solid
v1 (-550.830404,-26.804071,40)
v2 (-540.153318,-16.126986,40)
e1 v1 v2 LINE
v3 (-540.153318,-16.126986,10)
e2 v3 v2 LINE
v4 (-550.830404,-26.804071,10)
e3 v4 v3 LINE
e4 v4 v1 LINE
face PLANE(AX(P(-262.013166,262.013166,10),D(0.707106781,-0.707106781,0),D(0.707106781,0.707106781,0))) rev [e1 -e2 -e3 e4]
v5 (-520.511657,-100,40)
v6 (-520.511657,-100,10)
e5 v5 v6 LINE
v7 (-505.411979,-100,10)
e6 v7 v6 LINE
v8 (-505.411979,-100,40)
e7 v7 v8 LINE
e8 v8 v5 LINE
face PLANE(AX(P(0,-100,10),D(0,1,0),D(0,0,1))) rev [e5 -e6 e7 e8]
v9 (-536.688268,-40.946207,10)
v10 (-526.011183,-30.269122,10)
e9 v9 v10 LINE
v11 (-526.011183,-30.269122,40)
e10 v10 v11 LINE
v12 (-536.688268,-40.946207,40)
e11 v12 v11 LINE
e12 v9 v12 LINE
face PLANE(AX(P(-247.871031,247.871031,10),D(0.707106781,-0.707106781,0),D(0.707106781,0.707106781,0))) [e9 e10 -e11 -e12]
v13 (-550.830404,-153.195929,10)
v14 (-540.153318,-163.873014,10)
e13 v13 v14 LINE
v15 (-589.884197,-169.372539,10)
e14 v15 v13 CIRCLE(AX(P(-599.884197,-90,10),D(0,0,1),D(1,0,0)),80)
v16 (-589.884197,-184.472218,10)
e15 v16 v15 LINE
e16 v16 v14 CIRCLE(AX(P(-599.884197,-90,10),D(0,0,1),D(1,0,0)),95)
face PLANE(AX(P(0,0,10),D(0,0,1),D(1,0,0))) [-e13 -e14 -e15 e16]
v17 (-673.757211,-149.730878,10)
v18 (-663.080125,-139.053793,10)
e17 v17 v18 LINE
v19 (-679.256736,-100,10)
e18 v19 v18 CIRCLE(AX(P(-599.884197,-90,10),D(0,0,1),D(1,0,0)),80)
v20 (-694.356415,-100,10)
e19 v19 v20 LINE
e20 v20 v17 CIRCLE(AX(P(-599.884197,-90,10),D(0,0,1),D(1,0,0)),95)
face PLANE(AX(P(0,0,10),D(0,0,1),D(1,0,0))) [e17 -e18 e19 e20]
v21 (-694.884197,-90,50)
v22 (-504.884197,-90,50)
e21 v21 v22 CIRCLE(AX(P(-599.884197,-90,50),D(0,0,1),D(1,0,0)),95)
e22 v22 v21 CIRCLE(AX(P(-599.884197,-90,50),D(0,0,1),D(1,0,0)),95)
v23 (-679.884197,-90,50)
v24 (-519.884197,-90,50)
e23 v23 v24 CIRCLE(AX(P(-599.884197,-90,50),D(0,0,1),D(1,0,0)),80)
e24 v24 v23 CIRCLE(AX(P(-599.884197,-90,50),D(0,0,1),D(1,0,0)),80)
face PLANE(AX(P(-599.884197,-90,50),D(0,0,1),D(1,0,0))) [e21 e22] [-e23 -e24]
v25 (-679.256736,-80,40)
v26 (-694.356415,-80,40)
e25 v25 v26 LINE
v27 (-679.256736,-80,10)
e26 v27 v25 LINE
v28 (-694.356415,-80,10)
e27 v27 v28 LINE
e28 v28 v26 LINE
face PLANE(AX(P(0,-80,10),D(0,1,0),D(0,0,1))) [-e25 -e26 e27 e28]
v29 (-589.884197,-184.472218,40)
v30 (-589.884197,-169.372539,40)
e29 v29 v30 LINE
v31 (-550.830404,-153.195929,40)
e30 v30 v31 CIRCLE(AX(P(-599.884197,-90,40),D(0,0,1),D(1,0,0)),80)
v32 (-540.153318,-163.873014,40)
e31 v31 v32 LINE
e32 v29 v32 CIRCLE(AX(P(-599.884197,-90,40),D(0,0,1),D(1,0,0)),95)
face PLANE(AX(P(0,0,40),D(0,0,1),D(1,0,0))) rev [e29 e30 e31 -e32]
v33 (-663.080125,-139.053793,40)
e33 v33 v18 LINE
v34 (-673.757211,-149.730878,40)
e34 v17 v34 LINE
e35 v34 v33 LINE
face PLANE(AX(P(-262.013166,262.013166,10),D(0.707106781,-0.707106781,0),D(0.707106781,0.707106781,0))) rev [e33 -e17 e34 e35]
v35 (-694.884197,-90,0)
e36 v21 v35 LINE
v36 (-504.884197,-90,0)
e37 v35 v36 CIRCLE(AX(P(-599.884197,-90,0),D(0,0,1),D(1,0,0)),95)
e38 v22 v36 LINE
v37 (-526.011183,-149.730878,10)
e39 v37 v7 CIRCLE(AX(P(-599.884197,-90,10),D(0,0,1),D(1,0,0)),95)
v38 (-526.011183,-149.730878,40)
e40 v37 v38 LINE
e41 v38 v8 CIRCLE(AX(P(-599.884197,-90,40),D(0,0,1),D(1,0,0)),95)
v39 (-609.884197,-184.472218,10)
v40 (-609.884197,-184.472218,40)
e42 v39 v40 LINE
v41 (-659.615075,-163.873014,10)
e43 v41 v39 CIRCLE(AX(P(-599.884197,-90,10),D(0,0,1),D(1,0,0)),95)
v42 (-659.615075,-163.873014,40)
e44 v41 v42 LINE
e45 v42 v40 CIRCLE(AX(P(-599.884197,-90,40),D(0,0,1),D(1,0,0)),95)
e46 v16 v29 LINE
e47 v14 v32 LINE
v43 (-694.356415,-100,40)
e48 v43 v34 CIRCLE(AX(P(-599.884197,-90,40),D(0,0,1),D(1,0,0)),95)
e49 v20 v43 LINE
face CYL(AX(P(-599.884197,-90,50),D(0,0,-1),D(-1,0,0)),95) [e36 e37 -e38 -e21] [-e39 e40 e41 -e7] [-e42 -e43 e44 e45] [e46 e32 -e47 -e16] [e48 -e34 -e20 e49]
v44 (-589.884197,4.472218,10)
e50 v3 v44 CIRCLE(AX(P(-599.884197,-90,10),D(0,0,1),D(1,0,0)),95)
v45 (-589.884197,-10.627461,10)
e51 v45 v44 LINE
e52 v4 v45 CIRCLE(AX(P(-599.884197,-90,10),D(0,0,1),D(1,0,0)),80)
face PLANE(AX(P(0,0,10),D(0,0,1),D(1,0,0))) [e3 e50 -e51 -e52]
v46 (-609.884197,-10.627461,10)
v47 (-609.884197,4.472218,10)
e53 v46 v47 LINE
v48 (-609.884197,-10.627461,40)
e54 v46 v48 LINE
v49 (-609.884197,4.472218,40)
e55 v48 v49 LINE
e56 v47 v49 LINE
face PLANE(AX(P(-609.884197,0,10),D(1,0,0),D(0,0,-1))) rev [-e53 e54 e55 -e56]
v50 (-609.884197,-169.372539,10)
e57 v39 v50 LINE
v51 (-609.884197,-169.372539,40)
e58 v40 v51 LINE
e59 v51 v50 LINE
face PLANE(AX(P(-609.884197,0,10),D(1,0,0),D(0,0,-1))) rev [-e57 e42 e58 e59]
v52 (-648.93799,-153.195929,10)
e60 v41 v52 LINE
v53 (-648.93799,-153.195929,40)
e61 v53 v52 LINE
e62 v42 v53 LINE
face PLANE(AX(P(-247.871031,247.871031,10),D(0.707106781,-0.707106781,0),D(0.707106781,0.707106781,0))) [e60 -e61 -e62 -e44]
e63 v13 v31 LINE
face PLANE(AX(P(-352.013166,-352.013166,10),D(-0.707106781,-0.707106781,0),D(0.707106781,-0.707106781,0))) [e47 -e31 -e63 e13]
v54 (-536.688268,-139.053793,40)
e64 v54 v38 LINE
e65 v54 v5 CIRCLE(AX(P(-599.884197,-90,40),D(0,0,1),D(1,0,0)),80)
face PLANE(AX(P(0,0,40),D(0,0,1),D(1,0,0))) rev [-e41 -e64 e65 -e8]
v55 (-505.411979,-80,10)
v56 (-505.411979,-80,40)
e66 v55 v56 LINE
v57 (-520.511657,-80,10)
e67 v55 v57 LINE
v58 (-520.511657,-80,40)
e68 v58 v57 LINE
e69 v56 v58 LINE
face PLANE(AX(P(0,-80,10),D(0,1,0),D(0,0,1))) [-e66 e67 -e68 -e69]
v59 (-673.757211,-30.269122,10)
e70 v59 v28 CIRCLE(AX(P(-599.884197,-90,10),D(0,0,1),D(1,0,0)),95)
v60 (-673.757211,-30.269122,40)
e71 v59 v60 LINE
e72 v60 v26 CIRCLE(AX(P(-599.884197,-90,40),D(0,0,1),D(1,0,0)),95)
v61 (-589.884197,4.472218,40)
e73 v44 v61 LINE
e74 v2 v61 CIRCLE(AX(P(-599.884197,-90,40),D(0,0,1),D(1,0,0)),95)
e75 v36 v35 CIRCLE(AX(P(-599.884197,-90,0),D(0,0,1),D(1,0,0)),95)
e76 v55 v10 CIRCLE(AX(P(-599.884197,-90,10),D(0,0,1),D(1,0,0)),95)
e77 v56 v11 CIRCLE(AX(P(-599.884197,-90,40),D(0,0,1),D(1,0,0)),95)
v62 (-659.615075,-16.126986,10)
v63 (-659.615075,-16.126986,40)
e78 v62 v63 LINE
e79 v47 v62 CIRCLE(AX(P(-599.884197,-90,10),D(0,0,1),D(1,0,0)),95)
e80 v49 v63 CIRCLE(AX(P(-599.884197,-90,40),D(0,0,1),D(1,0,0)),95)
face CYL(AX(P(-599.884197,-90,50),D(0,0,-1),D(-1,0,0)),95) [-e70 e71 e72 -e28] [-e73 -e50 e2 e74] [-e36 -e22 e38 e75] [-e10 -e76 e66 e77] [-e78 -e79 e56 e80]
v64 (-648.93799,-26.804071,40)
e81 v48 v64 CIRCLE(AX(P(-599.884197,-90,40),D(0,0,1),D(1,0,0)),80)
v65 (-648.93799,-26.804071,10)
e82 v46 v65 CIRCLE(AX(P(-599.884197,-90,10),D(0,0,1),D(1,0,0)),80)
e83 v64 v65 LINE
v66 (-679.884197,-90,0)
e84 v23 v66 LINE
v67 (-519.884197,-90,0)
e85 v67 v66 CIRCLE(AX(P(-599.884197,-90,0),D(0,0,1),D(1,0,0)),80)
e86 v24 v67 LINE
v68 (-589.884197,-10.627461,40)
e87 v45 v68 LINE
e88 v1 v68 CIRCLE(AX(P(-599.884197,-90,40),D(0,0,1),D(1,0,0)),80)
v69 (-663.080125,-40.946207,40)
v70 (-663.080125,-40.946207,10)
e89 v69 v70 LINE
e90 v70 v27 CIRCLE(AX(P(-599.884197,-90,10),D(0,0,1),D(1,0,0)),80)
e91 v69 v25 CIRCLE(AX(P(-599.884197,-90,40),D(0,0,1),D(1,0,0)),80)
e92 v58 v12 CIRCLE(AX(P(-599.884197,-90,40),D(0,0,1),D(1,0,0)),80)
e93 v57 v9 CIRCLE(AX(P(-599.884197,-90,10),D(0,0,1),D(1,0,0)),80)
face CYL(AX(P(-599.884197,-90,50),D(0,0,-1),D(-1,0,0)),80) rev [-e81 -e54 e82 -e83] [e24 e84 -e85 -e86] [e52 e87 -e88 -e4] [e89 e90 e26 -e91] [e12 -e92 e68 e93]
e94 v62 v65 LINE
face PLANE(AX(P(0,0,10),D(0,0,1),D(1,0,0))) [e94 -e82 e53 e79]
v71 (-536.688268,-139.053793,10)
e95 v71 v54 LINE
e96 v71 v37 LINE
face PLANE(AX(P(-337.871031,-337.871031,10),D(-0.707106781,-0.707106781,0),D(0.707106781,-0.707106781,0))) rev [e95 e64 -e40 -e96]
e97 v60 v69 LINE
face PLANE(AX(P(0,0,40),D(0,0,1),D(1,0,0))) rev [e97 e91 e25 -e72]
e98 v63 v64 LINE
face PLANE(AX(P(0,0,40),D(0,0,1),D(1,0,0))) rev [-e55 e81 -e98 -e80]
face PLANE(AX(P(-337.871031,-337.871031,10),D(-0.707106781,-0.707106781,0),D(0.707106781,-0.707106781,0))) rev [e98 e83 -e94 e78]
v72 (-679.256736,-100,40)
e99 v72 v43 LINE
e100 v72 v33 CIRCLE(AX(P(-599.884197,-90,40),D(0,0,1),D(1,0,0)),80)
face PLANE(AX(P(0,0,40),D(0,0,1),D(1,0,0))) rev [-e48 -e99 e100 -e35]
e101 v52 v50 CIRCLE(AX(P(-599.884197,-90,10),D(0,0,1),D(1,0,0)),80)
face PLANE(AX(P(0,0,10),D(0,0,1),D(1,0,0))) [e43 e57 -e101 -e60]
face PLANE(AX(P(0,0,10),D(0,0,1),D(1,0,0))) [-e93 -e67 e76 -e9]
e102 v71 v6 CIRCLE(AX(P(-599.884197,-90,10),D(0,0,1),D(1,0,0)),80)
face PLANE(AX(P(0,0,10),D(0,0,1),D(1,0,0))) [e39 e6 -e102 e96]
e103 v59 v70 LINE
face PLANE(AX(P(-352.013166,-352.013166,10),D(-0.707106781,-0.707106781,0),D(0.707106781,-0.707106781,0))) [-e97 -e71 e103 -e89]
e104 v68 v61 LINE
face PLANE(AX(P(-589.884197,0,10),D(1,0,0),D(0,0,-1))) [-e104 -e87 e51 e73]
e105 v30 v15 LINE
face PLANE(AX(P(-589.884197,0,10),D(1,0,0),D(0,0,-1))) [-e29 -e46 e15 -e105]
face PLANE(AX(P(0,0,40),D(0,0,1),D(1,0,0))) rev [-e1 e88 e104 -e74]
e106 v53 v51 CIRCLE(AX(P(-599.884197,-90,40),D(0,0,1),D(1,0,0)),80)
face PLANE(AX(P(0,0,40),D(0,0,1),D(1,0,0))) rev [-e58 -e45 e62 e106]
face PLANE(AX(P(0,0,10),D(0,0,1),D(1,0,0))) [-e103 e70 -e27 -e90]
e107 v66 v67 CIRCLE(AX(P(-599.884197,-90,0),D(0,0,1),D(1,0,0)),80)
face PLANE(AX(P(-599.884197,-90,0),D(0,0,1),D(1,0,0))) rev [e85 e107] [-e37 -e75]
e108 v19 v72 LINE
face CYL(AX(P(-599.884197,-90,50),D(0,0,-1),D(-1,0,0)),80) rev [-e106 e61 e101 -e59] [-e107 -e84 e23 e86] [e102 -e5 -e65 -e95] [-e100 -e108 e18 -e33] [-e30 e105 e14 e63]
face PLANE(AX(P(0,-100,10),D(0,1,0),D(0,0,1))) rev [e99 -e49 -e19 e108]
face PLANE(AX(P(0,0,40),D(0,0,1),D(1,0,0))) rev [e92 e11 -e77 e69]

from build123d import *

# Parameters (mm, degrees)
SKETCH1_R           = 95
SKETCH1_R_2         = 80
BOSS_EXTRUDE1_DEPTH = 50
CUT_EXTRUDE1_START  = -40
SKETCH2_R           = 80
CUT_EXTRUDE1_DEPTH  = 30


with BuildPart() as part:
    # Sketch1 → Boss-Extrude1 (new body)
    with BuildSketch(Plane.XY):
        with Locations((-599.884196758, -90)):
            Circle(SKETCH1_R)
        with Locations((-599.884196758, -90)):
            Circle(SKETCH1_R_2, mode=Mode.SUBTRACT)
    extrude(amount=BOSS_EXTRUDE1_DEPTH)

    # Sketch2 → Cut-Extrude1 (cut)
    with BuildSketch(Plane.XY.offset(50).offset(CUT_EXTRUDE1_START)):
        with BuildLine():
            ThreePointArc((-679.25673609, -100), (-673.794559359, -120.614674589), (-663.080125372, -139.05379299))
            Line((-663.080125372, -139.05379299), (-624.026332382, -100))
            Line((-624.026332382, -100), (-679.25673609, -100))
        make_face()
        with BuildLine():
            ThreePointArc((-694.356414897, -100), (-687.652752347, -126.354926075), (-673.757210649, -149.730878268))
            Line((-673.757210649, -149.730878268), (-663.080125372, -139.05379299))
            ThreePointArc((-663.080125372, -139.05379299), (-673.794559359, -120.614674589), (-679.25673609, -100))
            Line((-679.25673609, -100), (-694.356414897, -100))
        make_face()
        with BuildLine():
            Line((-609.884196758, -114.142135624), (-648.937989748, -153.195928613))
            ThreePointArc((-648.937989748, -153.195928613), (-630.498871347, -163.910362601), (-609.884196758, -169.372539332))
            Line((-609.884196758, -169.372539332), (-609.884196758, -114.142135624))
        make_face()
        with BuildLine():
            Line((-648.937989748, -153.195928613), (-659.615075026, -163.873013891))
            ThreePointArc((-659.615075026, -163.873013891), (-636.239122833, -177.768555589), (-609.884196758, -184.472218138))
            Line((-609.884196758, -184.472218138), (-609.884196758, -169.372539332))
            ThreePointArc((-609.884196758, -169.372539332), (-630.498871347, -163.910362601), (-648.937989748, -153.195928613))
        make_face()
        with BuildLine():
            Line((-589.884196758, -169.372539332), (-589.884196758, -184.472218138))
            ThreePointArc((-589.884196758, -184.472218138), (-563.529270683, -177.768555589), (-540.15331849, -163.873013891))
            Line((-540.15331849, -163.873013891), (-550.830403768, -153.195928613))
            ThreePointArc((-550.830403768, -153.195928613), (-569.269522169, -163.910362601), (-589.884196758, -169.372539332))
        make_face()
        with BuildLine():
            Line((-589.884196758, -114.142135624), (-589.884196758, -169.372539332))
            ThreePointArc((-589.884196758, -169.372539332), (-569.269522169, -163.910362601), (-550.830403768, -153.195928613))
            Line((-550.830403768, -153.195928613), (-589.884196758, -114.142135624))
        make_face()
        with BuildLine():
            Line((-575.742061134, -100), (-536.688268145, -139.05379299))
            ThreePointArc((-536.688268145, -139.05379299), (-525.973834157, -120.614674589), (-520.511657426, -100))
            Line((-520.511657426, -100), (-575.742061134, -100))
        make_face()
        with BuildLine():
            Line((-536.688268145, -139.05379299), (-526.011182867, -149.730878268))
            ThreePointArc((-526.011182867, -149.730878268), (-512.115641169, -126.354926075), (-505.41197862, -100))
            Line((-505.41197862, -100), (-520.511657426, -100))
            ThreePointArc((-520.511657426, -100), (-525.973834157, -120.614674589), (-536.688268145, -139.05379299))
        make_face()
        with BuildLine():
            Line((-536.688268145, -40.94620701), (-575.742061134, -80))
            Line((-575.742061134, -80), (-520.511657426, -80))
            ThreePointArc((-520.511657426, -80), (-525.973834157, -59.385325411), (-536.688268145, -40.94620701))
        make_face()
        with BuildLine():
            Line((-520.511657426, -80), (-505.41197862, -80))
            ThreePointArc((-505.41197862, -80), (-512.115641169, -53.645073925), (-526.011182867, -30.269121732))
            Line((-526.011182867, -30.269121732), (-536.688268145, -40.94620701))
            ThreePointArc((-536.688268145, -40.94620701), (-525.973834157, -59.385325411), (-520.511657426, -80))
        make_face()
        with BuildLine():
            Line((-589.884196758, -10.627460668), (-589.884196758, -65.857864376))
            Line((-589.884196758, -65.857864376), (-550.830403768, -26.804071387))
            ThreePointArc((-550.830403768, -26.804071387), (-569.269522169, -16.089637399), (-589.884196758, -10.627460668))
        make_face()
        with BuildLine():
            ThreePointArc((-540.15331849, -16.126986109), (-563.529270683, -2.231444411), (-589.884196758, 4.472218138))
            Line((-589.884196758, 4.472218138), (-589.884196758, -10.627460668))
            ThreePointArc((-589.884196758, -10.627460668), (-569.269522169, -16.089637399), (-550.830403768, -26.804071387))
            Line((-550.830403768, -26.804071387), (-540.15331849, -16.126986109))
        make_face()
        with BuildLine():
            ThreePointArc((-609.884196758, -10.627460668), (-630.498871347, -16.089637399), (-648.937989748, -26.804071387))
            Line((-648.937989748, -26.804071387), (-609.884196758, -65.857864376))
            Line((-609.884196758, -65.857864376), (-609.884196758, -10.627460668))
        make_face()
        with BuildLine():
            ThreePointArc((-609.884196758, 4.472218138), (-636.239122833, -2.231444411), (-659.615075026, -16.126986109))
            Line((-659.615075026, -16.126986109), (-648.937989748, -26.804071387))
            ThreePointArc((-648.937989748, -26.804071387), (-630.498871347, -16.089637399), (-609.884196758, -10.627460668))
            Line((-609.884196758, -10.627460668), (-609.884196758, 4.472218138))
        make_face()
        with BuildLine():
            ThreePointArc((-673.757210649, -30.269121732), (-687.652752347, -53.645073925), (-694.356414897, -80))
            Line((-694.356414897, -80), (-679.25673609, -80))
            ThreePointArc((-679.25673609, -80), (-673.794559359, -59.385325411), (-663.080125372, -40.94620701))
            Line((-663.080125372, -40.94620701), (-673.757210649, -30.269121732))
        make_face()
        with BuildLine():
            ThreePointArc((-663.080125372, -40.94620701), (-673.794559359, -59.385325411), (-679.25673609, -80))
            Line((-679.25673609, -80), (-624.026332382, -80))
            Line((-624.026332382, -80), (-663.080125372, -40.94620701))
        make_face()
        with Locations((-599.884196758, -90)):
            Circle(SKETCH2_R)
    extrude(amount=CUT_EXTRUDE1_DEPTH, mode=Mode.SUBTRACT)


solid = part.part
